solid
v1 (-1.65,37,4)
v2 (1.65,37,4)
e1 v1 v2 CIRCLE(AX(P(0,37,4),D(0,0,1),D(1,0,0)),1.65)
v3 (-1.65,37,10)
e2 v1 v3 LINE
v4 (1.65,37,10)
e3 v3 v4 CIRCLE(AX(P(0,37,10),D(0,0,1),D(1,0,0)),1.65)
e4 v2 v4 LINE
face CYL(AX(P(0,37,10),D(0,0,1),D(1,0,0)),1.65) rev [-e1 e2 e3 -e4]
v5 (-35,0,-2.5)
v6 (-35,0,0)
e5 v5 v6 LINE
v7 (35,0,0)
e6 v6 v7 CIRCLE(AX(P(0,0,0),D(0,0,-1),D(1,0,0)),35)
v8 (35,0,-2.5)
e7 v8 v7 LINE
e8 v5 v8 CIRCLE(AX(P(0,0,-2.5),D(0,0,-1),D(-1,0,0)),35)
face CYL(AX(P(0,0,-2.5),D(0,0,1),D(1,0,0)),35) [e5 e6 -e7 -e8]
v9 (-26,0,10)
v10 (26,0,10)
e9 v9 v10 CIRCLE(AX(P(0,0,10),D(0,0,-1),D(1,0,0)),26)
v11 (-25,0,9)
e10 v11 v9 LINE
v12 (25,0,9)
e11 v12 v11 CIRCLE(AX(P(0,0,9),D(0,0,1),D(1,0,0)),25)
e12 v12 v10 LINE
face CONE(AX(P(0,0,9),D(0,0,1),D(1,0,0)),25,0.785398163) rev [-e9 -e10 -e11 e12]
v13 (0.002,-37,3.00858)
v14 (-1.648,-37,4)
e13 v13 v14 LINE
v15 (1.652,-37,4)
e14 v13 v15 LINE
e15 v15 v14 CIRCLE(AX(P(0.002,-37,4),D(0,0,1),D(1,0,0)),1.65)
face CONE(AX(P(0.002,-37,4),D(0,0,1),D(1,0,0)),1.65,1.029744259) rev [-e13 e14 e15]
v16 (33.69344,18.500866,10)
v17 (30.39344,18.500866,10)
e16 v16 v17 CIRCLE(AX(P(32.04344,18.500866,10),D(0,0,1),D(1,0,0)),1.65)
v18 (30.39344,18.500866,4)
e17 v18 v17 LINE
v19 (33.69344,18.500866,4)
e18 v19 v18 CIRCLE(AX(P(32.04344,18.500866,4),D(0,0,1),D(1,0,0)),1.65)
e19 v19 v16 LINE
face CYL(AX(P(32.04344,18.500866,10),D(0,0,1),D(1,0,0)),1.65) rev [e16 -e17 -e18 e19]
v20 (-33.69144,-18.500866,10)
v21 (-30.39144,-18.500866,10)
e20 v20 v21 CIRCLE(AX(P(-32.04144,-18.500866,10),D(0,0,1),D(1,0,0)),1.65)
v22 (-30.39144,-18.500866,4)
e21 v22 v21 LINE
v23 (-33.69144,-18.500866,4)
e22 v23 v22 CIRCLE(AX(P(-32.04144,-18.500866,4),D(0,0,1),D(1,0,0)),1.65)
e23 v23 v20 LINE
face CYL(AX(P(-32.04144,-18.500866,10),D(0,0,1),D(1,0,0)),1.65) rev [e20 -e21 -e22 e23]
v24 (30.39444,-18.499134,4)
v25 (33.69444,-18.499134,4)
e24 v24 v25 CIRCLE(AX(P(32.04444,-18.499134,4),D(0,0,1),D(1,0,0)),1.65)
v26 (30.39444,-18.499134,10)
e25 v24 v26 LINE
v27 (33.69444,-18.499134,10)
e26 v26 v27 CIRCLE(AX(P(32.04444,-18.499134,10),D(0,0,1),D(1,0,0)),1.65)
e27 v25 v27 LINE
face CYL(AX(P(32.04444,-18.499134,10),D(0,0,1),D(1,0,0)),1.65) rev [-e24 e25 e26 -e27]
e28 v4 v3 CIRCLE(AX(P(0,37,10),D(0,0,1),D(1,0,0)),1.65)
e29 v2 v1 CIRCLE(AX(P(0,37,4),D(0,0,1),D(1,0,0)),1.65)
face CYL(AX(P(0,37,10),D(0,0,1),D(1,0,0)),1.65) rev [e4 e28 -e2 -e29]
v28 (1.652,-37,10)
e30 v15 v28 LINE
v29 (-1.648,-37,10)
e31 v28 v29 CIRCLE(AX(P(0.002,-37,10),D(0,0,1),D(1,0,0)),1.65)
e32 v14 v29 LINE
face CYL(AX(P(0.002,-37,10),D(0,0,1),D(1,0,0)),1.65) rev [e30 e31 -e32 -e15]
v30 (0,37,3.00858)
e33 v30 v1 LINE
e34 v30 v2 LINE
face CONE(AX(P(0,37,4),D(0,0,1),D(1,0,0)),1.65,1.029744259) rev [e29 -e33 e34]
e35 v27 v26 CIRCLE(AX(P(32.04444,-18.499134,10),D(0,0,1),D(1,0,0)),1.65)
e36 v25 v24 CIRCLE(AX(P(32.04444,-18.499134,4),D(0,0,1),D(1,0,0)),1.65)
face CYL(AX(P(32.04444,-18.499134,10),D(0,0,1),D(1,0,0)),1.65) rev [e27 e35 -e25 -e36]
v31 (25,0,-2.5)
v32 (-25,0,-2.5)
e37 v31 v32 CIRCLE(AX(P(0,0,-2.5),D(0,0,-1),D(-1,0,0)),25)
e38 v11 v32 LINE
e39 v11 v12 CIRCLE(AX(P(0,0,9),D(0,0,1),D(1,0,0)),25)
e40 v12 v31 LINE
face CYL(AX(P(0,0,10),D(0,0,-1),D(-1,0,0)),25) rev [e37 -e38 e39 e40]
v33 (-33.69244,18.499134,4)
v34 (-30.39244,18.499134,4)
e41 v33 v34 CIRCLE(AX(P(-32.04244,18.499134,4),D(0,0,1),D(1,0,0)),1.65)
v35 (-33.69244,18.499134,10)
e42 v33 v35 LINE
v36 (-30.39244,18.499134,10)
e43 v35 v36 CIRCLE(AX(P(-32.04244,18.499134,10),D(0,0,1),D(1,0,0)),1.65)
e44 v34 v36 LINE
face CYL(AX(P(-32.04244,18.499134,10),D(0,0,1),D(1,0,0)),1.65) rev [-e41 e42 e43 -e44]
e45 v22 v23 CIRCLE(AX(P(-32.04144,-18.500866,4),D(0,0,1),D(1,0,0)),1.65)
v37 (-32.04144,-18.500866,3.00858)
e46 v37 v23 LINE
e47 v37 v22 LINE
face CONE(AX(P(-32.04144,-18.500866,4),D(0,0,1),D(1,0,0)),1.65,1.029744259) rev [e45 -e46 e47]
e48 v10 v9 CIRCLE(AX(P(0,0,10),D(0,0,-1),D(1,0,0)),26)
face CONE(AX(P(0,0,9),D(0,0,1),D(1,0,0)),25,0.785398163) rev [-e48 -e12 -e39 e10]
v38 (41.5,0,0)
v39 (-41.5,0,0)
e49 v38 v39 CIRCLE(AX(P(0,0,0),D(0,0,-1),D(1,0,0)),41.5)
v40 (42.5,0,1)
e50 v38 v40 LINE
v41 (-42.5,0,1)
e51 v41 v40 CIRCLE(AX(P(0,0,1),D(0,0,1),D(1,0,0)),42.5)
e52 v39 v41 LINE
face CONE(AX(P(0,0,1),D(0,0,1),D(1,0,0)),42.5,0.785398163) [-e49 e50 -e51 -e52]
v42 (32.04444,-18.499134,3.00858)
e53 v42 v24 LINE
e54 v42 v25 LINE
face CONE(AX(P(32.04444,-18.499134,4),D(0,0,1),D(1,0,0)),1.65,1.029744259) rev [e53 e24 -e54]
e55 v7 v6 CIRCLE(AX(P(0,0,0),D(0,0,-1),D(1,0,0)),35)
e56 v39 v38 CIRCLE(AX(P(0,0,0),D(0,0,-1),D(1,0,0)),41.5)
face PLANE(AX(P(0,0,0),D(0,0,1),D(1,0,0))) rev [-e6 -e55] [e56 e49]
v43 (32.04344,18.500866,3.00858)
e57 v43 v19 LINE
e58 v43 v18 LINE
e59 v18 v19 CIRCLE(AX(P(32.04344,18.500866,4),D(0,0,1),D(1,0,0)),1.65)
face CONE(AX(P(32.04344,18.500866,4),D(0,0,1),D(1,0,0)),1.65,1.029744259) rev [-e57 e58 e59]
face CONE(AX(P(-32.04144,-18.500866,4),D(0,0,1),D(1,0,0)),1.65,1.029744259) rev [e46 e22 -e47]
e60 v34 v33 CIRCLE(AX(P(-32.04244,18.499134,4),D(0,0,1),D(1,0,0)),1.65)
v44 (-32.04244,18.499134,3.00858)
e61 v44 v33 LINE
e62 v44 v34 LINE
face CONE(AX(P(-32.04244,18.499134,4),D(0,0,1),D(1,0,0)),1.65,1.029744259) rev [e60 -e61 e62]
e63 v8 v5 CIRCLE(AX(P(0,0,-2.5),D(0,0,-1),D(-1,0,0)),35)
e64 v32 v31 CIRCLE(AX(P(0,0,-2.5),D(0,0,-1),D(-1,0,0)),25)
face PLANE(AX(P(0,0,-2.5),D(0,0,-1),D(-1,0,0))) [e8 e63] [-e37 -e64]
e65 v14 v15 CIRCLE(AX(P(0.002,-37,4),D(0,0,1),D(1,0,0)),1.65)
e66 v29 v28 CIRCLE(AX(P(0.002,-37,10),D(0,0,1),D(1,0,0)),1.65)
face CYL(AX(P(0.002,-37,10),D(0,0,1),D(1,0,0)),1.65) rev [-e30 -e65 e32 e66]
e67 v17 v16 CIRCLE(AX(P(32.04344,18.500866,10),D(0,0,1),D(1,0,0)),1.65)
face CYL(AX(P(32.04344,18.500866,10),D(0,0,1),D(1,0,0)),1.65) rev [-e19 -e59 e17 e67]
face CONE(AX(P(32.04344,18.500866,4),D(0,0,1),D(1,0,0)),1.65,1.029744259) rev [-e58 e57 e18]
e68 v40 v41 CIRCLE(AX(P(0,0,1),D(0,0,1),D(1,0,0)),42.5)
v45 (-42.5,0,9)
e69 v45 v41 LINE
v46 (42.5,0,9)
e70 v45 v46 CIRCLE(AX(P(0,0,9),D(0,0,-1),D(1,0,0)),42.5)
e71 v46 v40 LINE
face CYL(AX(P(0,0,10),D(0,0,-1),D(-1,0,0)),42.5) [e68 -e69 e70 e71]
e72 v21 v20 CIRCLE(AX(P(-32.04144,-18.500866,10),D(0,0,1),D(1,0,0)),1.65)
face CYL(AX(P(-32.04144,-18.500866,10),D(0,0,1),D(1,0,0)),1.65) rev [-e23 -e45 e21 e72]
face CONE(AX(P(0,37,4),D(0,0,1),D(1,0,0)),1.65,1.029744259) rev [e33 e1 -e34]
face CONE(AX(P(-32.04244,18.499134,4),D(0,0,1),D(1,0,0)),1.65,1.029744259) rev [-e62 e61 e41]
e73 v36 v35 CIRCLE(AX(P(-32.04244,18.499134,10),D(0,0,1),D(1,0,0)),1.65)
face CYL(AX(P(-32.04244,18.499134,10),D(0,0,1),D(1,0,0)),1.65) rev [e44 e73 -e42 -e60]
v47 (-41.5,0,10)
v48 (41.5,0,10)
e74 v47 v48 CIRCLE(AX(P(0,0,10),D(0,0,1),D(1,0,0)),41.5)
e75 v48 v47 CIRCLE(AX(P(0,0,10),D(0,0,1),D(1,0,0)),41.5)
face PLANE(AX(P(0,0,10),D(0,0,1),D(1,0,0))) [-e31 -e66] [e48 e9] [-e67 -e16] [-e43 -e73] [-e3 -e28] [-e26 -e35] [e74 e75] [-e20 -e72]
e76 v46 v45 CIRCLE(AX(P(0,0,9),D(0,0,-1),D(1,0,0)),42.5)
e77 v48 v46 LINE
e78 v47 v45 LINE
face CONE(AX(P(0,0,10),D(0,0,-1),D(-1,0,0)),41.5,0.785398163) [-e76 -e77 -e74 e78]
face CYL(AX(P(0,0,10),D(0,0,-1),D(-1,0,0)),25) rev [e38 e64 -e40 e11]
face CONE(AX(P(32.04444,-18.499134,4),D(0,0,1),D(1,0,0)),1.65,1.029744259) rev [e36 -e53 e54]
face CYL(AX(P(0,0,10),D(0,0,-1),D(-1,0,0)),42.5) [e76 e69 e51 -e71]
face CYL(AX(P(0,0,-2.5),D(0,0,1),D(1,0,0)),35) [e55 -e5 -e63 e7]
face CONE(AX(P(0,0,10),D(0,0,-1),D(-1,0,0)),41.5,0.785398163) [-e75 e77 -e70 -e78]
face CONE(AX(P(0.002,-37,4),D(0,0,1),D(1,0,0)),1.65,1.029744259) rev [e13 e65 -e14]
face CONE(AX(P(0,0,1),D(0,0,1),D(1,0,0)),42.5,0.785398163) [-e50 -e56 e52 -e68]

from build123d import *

# Parameters (mm, degrees)
SKETCH1_R                 = 42.5
SKETCH1_R_2               = 25
BOSS_EXTRUDE1_DEPTH       = 10
CHAMFER1_SIZE             = 1
M4X0_7_TAPPED_HOLE1_D     = 3.3
M4X0_7_TAPPED_HOLE1_DEPTH = 6
M4X0_7_TAPPED_HOLE1_TIP   = 0.991420021
BOSS_EXTRUDE2_START       = 2.5
SKETCH5_R                 = 35
SKETCH5_R_2               = 25
BOSS_EXTRUDE2_DEPTH       = 2.5


with BuildPart() as part:
    # Sketch1 → Boss-Extrude1 (new body)
    with BuildSketch(Plane.XY):
        Circle(SKETCH1_R)
        Circle(SKETCH1_R_2, mode=Mode.SUBTRACT)
    extrude(amount=BOSS_EXTRUDE1_DEPTH)

    # Chamfer1
    chamfer1_edges = [part.edges().sort_by_distance(p)[0] for p in [
        (-42.5, 0, 0),
        (-42.5, 0, 10),
        (-25, 0, 10),
    ]]
    chamfer(chamfer1_edges, length=CHAMFER1_SIZE)

    # M4x0.7 Tapped Hole1
    with Locations(Plane(origin=(0, 37, 10), x_dir=(1, 0, 0), z_dir=(0, 0, 1))):
        with Locations((0, 0), (32.04343994, -18.499133975), (32.04443994, -55.499133975), (0.002, -74), (-32.04143994, -55.500866025), (-32.04243994, -18.500866025)):
            Hole(M4X0_7_TAPPED_HOLE1_D / 2, depth=M4X0_7_TAPPED_HOLE1_DEPTH)
            with Locations((0, 0, -(M4X0_7_TAPPED_HOLE1_DEPTH + M4X0_7_TAPPED_HOLE1_TIP / 2))):  # 118° drill point
                Cone(0, M4X0_7_TAPPED_HOLE1_D / 2, M4X0_7_TAPPED_HOLE1_TIP, mode=Mode.SUBTRACT)

    # Sketch5 → Boss-Extrude2 (add)
    with BuildSketch(Plane(origin=(0, 0, 0), x_dir=(-1, 0, 0), z_dir=(0, 0, -1)).offset(BOSS_EXTRUDE2_START)):
        with Locations(Location((0, 0, 0), (0, 0, 180))):
            Circle(SKETCH5_R)
        Circle(SKETCH5_R_2, mode=Mode.SUBTRACT)
    extrude(amount=-BOSS_EXTRUDE2_DEPTH)


solid = part.part
